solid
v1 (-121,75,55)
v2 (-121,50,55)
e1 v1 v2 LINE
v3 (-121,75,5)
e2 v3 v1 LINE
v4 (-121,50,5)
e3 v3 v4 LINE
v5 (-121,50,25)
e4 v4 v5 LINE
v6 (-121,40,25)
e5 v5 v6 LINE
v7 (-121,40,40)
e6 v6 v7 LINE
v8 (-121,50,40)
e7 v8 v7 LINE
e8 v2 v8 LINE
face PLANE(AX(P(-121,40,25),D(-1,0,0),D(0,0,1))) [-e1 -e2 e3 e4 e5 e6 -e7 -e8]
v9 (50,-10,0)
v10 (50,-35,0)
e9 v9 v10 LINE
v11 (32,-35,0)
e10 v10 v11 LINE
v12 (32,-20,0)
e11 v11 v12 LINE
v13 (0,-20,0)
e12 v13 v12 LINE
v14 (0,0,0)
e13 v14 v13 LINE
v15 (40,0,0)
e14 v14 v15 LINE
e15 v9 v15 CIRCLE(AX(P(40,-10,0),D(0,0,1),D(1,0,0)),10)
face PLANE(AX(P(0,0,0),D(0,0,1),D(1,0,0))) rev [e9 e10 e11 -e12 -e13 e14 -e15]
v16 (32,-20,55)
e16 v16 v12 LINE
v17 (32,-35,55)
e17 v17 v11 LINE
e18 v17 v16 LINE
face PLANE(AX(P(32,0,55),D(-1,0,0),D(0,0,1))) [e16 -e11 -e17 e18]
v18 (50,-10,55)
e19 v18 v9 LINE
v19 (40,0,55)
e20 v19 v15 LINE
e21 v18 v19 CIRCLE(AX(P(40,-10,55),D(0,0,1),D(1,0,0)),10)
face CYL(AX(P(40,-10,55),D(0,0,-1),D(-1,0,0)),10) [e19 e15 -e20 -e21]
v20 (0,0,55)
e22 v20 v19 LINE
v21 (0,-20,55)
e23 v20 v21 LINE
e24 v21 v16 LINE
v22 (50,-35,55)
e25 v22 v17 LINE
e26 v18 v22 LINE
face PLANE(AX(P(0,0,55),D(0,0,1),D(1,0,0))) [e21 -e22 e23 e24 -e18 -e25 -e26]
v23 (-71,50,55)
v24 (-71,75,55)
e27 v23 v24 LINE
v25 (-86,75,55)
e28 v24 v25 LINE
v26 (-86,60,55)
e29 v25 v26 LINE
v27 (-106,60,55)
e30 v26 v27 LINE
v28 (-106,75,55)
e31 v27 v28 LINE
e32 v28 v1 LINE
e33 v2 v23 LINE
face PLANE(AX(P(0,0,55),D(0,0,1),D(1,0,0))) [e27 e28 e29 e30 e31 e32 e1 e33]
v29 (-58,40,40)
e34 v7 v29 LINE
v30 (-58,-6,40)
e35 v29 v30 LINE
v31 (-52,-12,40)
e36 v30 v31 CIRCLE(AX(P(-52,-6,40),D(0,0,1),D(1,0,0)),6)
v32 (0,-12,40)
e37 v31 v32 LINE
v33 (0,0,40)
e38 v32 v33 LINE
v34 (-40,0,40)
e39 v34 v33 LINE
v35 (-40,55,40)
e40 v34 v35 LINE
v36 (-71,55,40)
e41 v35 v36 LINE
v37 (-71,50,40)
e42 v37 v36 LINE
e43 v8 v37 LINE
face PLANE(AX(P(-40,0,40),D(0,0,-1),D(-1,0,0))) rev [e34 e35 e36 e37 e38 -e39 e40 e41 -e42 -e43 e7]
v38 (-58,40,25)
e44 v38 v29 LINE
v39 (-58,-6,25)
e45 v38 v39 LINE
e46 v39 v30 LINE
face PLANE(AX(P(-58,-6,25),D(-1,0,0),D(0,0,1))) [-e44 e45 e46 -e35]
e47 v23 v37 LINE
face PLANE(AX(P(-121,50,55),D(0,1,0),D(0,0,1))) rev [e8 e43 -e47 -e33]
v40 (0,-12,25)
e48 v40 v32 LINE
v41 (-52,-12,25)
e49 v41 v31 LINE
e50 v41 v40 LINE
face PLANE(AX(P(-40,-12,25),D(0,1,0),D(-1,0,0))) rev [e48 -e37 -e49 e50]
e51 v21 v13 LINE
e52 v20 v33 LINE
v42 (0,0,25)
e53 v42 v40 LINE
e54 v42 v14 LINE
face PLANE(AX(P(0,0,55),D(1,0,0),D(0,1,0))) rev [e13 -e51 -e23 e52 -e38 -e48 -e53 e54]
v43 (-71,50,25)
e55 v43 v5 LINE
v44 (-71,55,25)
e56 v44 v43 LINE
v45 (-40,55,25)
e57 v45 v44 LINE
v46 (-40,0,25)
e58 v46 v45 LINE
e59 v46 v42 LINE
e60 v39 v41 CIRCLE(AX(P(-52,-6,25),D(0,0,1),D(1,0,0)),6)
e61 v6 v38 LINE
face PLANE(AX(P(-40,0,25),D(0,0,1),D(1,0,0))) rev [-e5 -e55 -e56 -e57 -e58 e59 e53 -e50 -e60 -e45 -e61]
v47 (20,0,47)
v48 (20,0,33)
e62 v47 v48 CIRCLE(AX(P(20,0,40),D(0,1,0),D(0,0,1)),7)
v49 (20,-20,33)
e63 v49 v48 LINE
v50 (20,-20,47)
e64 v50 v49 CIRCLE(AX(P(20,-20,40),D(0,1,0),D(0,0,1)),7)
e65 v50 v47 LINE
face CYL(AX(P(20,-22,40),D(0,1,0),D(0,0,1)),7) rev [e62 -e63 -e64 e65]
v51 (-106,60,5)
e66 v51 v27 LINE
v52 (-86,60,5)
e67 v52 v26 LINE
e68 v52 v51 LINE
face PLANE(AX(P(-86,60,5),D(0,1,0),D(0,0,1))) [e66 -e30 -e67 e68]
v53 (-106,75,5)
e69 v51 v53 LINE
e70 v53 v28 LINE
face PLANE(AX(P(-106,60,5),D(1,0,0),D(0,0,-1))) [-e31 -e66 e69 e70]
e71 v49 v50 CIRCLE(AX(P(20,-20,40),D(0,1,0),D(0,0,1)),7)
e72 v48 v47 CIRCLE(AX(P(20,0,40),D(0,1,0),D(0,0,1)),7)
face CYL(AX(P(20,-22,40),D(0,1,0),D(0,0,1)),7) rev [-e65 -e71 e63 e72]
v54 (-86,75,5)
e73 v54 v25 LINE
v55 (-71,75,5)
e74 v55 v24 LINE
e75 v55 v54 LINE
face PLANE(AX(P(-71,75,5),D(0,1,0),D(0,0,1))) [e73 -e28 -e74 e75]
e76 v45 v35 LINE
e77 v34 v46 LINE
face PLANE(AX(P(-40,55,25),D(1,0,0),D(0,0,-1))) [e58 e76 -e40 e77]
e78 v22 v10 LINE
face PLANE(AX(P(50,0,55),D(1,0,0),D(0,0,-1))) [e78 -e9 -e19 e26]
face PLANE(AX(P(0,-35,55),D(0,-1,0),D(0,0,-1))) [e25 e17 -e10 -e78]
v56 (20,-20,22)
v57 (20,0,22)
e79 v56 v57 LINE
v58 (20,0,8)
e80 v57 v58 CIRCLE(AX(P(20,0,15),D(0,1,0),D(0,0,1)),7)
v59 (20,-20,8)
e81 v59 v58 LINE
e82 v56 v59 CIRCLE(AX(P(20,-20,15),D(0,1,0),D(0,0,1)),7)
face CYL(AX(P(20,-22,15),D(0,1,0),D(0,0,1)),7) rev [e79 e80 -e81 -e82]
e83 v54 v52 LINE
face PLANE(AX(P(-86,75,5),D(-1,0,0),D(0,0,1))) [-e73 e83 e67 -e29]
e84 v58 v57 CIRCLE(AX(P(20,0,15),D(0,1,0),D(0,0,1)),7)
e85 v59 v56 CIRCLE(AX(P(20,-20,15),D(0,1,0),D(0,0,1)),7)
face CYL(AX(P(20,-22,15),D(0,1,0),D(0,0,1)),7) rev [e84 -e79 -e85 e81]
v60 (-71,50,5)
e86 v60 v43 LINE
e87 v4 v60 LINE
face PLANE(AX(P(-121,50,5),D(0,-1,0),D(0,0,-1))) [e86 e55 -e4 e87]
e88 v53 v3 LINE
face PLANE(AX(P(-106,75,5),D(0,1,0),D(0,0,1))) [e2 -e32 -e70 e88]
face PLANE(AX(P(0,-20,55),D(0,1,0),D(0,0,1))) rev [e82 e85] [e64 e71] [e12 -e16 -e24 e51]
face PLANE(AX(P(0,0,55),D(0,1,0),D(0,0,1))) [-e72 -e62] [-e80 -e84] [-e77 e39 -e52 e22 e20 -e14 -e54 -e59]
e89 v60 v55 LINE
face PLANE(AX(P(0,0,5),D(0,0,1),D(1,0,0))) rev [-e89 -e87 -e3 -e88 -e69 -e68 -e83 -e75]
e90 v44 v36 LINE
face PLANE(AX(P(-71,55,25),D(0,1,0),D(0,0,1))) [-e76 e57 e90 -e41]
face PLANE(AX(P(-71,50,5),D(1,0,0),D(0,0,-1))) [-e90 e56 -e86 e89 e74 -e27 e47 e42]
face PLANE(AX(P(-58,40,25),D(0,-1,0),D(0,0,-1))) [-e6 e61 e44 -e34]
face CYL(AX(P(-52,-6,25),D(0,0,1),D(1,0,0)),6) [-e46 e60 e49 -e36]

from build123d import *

# Parameters (mm, degrees)
BASE_BLOCK_DEPTH            = 55
HOLES_SKETCH_R              = 7
HOLES_2X_14_DEPTH           = 22
ARM_RISER_SKETCH_W          = 15
ARM_RISER_SKETCH_H          = 12
ARM_RISER_DEPTH             = 40
OFFSET_ARM_DEPTH            = 15
SLOTTED_CLAMP_BLOCK_DEPTH   = 35
CLAMP_BLOCK_EXTENSION_DEPTH = 15


with BuildPart() as part:
    # Base Block Profile → Base Block (new body)
    with BuildSketch(Plane.XY):
        with BuildLine():
            Line((50, -10), (50, -35))
            Line((50, -35), (32, -35))
            Line((32, -35), (32, -20))
            Line((32, -20), (0, -20))
            Line((0, -20), (0, 0))
            Line((0, 0), (40, 0))
            ThreePointArc((40, 0), (47.071067812, -2.928932188), (50, -10))
        make_face()
    extrude(amount=BASE_BLOCK_DEPTH)

    # Holes Sketch → Holes 2x_14 (cut)
    with BuildSketch(Plane(origin=(0, 0, 0), x_dir=(1, 0, 0), z_dir=(0, 1, 0))):
        with Locations(Location((20, -15, 0), (0, 0, 270))):
            Circle(HOLES_SKETCH_R)
        with Locations(Location((20, -40, 0), (0, 0, 270))):
            Circle(HOLES_SKETCH_R)
    extrude(amount=-HOLES_2X_14_DEPTH, mode=Mode.SUBTRACT)

    # Arm Riser Sketch → Arm Riser (add)
    with BuildSketch(Plane.ZY):
        with Locations((32.5, -6)):
            Rectangle(ARM_RISER_SKETCH_W, ARM_RISER_SKETCH_H)
    extrude(amount=ARM_RISER_DEPTH)

    # Offset Arm Profile → Offset Arm (add)
    with BuildSketch(Plane.XY.offset(40)):
        with BuildLine():
            Line((-40, -12), (-52, -12))
            ThreePointArc((-52, -12), (-56.242640687, -10.242640687), (-58, -6))
            Line((-58, -6), (-58, 40))
            Line((-58, 40), (-121, 40))
            Line((-121, 40), (-121, 50))
            Line((-121, 50), (-71, 50))
            Line((-71, 50), (-71, 55))
            Line((-71, 55), (-40, 55))
            Line((-40, 55), (-40, 0))
            Line((-40, 0), (0, 0))
            Line((0, 0), (0, -12))
            Line((0, -12), (-40, -12))
        make_face()
    extrude(amount=-OFFSET_ARM_DEPTH)

    # Slotted Clamp Block Profile → Slotted Clamp Block (add)
    with BuildSketch(Plane.XY.offset(40)):
        Polygon((-121, 50), (-71, 50), (-71, 75), (-86, 75), (-86, 60), (-106, 60), (-106, 75), (-121, 75), align=None)
    extrude(amount=-SLOTTED_CLAMP_BLOCK_DEPTH)

    # Clamp Block Extension Profile → Clamp Block Extension (add)
    with BuildSketch(Plane.XY.offset(40)):
        Polygon((-121, 75), (-121, 50), (-71, 50), (-71, 75), (-86, 75), (-86, 60), (-106, 60), (-106, 75), align=None)
    extrude(amount=CLAMP_BLOCK_EXTENSION_DEPTH)


solid = part.part
